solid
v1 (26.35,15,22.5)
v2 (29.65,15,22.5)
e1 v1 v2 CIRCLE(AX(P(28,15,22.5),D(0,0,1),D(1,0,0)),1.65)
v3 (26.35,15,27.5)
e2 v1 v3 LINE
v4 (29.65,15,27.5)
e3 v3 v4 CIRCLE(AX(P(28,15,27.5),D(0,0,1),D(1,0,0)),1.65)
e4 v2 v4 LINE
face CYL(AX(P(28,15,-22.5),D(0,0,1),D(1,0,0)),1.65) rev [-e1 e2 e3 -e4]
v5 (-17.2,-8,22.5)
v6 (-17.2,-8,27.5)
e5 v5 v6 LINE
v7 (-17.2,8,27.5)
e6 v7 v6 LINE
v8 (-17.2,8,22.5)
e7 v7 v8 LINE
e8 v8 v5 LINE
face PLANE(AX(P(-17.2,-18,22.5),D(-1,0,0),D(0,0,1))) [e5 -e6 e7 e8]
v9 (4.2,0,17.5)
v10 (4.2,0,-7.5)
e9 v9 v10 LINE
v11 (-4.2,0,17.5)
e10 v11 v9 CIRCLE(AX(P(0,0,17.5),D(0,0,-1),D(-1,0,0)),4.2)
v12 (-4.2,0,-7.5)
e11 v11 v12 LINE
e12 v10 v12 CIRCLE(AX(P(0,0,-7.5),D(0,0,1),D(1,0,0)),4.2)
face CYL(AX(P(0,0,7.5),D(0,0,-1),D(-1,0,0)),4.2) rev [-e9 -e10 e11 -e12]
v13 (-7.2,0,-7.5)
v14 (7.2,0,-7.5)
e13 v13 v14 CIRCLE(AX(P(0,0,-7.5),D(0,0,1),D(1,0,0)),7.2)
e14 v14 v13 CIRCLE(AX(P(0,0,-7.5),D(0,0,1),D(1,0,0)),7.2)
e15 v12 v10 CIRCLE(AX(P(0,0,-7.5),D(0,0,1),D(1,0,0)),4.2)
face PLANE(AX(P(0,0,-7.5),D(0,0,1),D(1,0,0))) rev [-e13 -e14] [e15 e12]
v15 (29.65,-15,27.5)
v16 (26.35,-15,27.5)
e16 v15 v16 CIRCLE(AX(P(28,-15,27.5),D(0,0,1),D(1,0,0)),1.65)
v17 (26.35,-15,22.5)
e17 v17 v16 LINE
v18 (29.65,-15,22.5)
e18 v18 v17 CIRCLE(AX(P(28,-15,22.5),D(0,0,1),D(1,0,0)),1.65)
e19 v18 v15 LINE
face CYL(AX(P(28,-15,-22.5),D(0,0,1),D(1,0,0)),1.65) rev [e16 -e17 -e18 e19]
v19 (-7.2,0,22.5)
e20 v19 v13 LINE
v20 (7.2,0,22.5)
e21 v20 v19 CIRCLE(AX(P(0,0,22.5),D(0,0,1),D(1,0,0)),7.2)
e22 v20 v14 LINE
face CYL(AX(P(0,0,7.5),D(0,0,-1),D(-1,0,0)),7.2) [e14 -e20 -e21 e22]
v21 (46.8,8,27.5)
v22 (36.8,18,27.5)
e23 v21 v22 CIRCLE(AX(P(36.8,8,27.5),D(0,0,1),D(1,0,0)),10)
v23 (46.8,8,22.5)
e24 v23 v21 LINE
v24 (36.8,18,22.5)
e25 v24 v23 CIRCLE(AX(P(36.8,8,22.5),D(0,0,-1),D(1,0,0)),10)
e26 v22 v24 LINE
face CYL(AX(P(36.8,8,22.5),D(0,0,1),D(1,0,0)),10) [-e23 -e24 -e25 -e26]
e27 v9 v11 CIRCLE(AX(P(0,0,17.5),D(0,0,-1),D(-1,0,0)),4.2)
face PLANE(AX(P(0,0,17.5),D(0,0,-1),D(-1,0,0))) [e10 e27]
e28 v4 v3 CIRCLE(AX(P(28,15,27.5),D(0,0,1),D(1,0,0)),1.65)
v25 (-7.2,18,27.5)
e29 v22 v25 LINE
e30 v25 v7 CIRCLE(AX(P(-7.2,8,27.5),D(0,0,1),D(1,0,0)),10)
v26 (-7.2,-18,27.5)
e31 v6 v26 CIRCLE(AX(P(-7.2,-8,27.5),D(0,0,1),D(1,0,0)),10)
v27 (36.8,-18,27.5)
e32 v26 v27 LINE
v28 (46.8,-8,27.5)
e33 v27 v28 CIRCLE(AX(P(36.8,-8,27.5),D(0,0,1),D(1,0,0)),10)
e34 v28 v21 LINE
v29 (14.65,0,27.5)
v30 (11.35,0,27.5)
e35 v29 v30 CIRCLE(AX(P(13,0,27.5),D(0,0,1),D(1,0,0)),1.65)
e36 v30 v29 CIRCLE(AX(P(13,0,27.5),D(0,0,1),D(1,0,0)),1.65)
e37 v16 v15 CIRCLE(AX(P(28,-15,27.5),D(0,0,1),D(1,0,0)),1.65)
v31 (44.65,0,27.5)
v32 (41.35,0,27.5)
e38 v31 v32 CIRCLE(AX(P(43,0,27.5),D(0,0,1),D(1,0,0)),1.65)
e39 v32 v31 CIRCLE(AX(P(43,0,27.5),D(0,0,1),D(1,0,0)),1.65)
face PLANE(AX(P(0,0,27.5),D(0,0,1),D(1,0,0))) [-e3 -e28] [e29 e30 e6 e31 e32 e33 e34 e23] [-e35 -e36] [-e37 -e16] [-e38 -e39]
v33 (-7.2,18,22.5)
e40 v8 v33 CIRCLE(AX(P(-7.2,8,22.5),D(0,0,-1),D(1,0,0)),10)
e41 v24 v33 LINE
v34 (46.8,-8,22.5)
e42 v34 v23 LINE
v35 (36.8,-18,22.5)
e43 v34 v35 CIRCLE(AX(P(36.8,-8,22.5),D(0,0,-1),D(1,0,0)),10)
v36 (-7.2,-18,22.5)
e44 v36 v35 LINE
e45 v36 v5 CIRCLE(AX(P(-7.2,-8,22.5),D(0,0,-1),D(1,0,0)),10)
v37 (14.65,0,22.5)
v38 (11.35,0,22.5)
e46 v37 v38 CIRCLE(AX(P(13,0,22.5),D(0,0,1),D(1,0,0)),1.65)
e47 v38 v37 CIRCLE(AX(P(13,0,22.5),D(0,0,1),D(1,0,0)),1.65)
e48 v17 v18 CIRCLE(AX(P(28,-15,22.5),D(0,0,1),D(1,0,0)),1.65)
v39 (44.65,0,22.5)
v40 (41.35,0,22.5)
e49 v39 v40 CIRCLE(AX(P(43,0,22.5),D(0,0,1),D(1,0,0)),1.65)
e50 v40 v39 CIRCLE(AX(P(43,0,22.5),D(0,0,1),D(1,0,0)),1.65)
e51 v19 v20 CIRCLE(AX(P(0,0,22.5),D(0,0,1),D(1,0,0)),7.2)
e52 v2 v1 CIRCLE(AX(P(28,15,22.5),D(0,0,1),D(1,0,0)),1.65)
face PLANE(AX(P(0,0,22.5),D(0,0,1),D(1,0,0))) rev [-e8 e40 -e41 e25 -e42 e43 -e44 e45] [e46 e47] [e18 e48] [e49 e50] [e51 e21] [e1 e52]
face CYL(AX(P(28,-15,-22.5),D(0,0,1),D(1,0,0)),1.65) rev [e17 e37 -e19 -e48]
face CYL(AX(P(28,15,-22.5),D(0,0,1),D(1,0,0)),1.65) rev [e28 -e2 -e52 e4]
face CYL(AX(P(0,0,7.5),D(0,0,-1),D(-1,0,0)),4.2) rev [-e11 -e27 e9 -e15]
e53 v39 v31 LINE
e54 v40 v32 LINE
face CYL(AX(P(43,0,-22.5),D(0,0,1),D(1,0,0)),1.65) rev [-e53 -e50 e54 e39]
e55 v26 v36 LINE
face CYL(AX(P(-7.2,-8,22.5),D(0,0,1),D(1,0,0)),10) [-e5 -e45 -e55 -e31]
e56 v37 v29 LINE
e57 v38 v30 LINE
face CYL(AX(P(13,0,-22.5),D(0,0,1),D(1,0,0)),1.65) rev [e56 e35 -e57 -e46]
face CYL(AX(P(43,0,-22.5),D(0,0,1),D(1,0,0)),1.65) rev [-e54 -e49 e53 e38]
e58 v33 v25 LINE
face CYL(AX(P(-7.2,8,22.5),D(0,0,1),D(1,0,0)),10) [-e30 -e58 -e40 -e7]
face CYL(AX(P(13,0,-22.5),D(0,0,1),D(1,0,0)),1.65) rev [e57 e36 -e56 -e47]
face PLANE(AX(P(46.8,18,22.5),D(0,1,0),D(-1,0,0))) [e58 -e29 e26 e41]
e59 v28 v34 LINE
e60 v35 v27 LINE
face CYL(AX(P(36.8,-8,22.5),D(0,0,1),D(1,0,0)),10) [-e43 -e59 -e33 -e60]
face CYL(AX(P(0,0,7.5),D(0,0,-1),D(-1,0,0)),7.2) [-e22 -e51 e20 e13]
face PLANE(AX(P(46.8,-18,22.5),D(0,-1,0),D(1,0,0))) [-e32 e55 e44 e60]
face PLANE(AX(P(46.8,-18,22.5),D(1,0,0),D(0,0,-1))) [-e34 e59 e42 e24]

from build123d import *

# Parameters (mm, degrees)
SKETCH_1_R               = 7.2
SKETCH_1_R_2             = 4.2
EXTRUDE_1_DEPTH          = 7.5
EXTRUDE_START            = 20
SKETCH_2_R               = 7.2
EXTRUDE_2_DEPTH          = 20
SKETCH_3_R               = 17.2
SKETCH_3_R_2             = 7.2
EXTRUDE_3_DEPTH          = 3
SKETCH_4_R               = 1.65
CUT_EXTRUDE_1_DEPTH      = 3
PATTERN_CIRCULAR_1_COUNT = 4
SKETCH_5_W               = 64
SKETCH_5_H               = 36
EXTRUDE_4_DEPTH          = 5
SKETCH_6_R               = 1.65
CUT_EXTRUDE_2_DEPTH      = 50
FILLET_1_R               = 10
SKETCH_7_R               = 4.2
CUT_EXTRUDE_3_DEPTH      = 10


with BuildPart() as part:
    # 草图1 → 凸台-拉伸1 (new, symmetric)
    with BuildSketch(Plane.XY):
        Circle(SKETCH_1_R)
        Circle(SKETCH_1_R_2, mode=Mode.SUBTRACT)
    extrude(amount=EXTRUDE_1_DEPTH, both=True)

    # 草图2 → 凸台-拉伸2 (add)
    with BuildSketch(Plane.XY.offset(7.5).offset(EXTRUDE_START)):
        Circle(SKETCH_2_R)
    extrude(amount=-EXTRUDE_2_DEPTH)

    # 草图3 → 凸台-拉伸3 (add)
    with BuildSketch(Plane.XY.offset(27.5)):
        Circle(SKETCH_3_R)
        Circle(SKETCH_3_R_2, mode=Mode.SUBTRACT)
    extrude(amount=-EXTRUDE_3_DEPTH)

    # 草图4 → 切除-拉伸1 (cut)
    with BuildSketch(Plane(origin=(0, 0, 24.5), x_dir=(-1, 0, 0), z_dir=(0, 0, -1))):
        with Locations((0, 15)):
            Circle(SKETCH_4_R)
    cut_extrude_1 = extrude(amount=-CUT_EXTRUDE_1_DEPTH, mode=Mode.SUBTRACT)

    # 阵列(圆周)1: 切除-拉伸1 ×4 about axis
    pattern_circular_1_axis = Axis((0, 0, 0), (0, 0, 1))
    for i in range(1, PATTERN_CIRCULAR_1_COUNT):
        add(cut_extrude_1.rotate(pattern_circular_1_axis, i * 360 / PATTERN_CIRCULAR_1_COUNT), mode=Mode.SUBTRACT)

    # 草图5 → 凸台-拉伸4 (add)
    with BuildSketch(Plane.XY.offset(27.5)):
        with Locations((14.8, 0)):
            Rectangle(SKETCH_5_W, SKETCH_5_H)
    extrude(amount=-EXTRUDE_4_DEPTH)

    # 草图6 → 切除-拉伸2 (cut)
    with BuildSketch(Plane.XY.offset(27.5)):
        with Locations((28, 15)):
            Circle(SKETCH_6_R)
        with Locations((43, 0)):
            Circle(SKETCH_6_R)
        with Locations((28, -15)):
            Circle(SKETCH_6_R)
        with Locations((13, 0)):
            Circle(SKETCH_6_R)
    extrude(amount=-CUT_EXTRUDE_2_DEPTH, mode=Mode.SUBTRACT)

    # 圆角1
    fillet_1_edges = [part.edges().sort_by_distance(p)[0] for p in [
        (-17.2, -18, 25),
        (-17.2, 18, 25),
        (46.8, 18, 25),
        (46.8, -18, 25),
    ]]
    fillet(fillet_1_edges, radius=FILLET_1_R)

    # 草图7 → 切除-拉伸3 (cut)
    with BuildSketch(Plane(origin=(0, 0, 7.5), x_dir=(-1, 0, 0), z_dir=(0, 0, -1))):
        Circle(SKETCH_7_R)
    extrude(amount=-CUT_EXTRUDE_3_DEPTH, mode=Mode.SUBTRACT)


solid = part.part
